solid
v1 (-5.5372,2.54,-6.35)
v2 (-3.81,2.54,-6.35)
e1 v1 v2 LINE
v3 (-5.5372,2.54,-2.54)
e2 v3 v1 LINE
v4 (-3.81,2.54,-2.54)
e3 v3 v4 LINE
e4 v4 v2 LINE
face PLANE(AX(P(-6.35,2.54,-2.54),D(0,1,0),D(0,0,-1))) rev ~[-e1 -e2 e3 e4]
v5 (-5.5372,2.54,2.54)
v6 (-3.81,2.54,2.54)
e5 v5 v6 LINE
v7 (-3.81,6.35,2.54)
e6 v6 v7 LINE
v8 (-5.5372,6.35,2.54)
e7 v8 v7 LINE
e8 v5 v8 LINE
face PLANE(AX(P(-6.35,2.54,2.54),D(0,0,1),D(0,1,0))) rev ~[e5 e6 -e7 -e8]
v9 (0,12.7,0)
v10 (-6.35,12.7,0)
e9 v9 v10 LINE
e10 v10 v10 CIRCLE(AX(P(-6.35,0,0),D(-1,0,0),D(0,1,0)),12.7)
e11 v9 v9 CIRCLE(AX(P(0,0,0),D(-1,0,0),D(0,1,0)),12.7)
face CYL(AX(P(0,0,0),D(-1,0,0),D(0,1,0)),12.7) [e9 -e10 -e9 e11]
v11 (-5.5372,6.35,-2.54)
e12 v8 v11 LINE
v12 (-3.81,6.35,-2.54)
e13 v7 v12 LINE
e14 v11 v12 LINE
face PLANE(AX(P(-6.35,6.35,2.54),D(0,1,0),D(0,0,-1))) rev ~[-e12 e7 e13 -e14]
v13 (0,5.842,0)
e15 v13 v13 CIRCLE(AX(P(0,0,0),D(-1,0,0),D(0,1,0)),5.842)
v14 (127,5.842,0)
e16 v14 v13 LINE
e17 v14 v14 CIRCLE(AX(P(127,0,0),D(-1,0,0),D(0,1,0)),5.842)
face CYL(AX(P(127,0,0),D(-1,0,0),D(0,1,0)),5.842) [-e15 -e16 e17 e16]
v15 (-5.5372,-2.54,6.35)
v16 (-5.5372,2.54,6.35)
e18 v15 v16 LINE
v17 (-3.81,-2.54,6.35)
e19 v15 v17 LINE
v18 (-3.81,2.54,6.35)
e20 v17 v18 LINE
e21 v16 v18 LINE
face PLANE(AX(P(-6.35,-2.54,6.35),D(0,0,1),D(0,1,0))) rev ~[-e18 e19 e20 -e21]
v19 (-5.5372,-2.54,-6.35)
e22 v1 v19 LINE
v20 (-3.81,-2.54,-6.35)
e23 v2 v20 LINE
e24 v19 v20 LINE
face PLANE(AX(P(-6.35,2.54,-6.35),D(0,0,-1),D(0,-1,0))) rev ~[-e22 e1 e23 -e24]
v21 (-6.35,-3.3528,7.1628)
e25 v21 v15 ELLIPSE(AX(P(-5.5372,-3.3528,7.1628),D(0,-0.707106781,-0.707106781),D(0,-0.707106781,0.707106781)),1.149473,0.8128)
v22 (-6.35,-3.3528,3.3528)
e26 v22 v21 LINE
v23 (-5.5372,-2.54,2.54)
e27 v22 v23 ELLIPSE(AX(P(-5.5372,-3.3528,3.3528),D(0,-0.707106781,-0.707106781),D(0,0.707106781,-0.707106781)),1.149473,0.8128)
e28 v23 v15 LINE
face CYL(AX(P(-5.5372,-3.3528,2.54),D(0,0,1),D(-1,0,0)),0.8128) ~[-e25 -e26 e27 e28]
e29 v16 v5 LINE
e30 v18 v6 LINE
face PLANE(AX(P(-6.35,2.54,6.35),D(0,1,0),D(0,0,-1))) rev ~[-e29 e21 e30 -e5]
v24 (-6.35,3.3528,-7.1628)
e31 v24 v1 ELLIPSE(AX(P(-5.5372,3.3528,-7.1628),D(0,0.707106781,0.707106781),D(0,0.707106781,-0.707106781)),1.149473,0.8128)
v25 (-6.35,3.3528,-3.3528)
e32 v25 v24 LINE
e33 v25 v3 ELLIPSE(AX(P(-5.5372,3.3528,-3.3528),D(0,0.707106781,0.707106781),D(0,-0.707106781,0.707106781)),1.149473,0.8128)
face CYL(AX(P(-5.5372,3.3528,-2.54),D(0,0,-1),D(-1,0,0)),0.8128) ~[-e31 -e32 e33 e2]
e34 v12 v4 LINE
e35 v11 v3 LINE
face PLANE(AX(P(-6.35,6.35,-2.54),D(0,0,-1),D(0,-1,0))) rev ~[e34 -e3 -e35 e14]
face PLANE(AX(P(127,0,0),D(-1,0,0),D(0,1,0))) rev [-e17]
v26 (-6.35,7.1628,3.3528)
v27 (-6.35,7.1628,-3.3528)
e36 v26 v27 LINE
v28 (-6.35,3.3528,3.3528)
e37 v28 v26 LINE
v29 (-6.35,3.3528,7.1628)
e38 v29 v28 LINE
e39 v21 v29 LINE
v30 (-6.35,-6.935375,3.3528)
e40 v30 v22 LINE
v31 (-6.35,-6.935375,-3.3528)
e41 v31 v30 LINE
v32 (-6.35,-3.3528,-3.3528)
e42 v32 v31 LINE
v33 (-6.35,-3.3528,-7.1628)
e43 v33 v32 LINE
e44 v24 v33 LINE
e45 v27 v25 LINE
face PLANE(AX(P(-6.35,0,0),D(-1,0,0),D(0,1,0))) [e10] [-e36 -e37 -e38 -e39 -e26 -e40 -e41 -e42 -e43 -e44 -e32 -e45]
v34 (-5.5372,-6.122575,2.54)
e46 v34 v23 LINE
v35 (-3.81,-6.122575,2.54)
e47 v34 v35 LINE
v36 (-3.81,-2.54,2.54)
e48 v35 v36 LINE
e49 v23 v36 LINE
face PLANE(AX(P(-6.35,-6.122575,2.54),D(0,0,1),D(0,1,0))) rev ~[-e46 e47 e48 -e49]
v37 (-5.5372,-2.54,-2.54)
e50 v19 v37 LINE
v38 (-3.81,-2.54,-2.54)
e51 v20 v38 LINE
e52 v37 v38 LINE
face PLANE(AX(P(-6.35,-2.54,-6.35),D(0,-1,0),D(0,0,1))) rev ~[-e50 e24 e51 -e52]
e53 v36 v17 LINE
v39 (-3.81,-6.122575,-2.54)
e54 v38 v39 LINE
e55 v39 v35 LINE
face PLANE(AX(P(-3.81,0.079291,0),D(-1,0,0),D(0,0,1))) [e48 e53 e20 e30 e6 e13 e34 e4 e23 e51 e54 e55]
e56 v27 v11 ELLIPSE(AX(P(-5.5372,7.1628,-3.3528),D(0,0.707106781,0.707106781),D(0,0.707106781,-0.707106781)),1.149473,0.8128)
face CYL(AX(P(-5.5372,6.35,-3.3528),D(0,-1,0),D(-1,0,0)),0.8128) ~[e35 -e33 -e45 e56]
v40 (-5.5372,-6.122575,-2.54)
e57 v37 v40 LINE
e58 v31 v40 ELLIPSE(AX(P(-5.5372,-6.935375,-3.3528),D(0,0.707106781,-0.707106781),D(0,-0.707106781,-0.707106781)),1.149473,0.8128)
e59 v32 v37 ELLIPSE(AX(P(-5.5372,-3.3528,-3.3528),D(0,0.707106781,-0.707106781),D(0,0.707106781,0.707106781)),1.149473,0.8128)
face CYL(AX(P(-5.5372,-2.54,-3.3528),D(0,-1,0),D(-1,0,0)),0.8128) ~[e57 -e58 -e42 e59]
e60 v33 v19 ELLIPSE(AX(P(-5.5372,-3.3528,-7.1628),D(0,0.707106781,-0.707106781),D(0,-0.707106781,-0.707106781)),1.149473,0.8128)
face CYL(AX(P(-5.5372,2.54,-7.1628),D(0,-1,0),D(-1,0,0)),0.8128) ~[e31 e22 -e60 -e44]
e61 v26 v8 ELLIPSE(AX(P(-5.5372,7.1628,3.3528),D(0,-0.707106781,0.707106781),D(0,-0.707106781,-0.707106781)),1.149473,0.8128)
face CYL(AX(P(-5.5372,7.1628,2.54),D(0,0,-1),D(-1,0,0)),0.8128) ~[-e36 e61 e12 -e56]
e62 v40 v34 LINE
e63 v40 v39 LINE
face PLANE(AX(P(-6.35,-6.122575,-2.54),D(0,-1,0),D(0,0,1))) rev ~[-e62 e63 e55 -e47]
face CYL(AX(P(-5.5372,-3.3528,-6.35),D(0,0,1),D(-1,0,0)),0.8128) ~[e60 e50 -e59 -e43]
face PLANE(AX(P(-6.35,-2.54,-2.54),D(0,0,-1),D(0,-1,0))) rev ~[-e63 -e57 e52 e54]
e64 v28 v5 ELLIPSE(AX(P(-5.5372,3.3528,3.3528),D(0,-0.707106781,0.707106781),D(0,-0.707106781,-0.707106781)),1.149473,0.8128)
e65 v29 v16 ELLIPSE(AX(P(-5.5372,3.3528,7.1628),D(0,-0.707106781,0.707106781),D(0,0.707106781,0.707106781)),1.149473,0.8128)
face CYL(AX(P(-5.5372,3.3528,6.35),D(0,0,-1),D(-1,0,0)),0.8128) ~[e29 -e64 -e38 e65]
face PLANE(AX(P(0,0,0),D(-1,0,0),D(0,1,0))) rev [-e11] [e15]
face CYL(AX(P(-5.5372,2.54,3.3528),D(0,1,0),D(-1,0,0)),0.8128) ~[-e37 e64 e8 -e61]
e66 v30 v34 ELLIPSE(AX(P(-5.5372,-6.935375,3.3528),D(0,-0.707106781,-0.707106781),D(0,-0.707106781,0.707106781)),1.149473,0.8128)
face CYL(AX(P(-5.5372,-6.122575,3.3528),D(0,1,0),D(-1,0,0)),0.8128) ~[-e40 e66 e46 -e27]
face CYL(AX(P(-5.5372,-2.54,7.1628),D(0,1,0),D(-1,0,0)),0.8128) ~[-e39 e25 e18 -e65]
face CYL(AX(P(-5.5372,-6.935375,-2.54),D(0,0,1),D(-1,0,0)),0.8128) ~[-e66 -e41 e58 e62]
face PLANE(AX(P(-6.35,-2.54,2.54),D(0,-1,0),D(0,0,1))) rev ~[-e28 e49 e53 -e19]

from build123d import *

# Parameters (mm, degrees)
CUT_EXTRUDE1_DEPTH = 2.54
FILLET2_R          = 0.8128


with BuildPart() as part:
    # Sketch1 → Revolve1 (revolve)
    with BuildSketch(Plane.XY):
        Polygon((0, 5.842), (0, 12.7), (-6.35, 12.7), (-6.35, 0), (0, 0), (127, 0), (127, 5.842), align=None)
    revolve(axis=Axis((127, 0, 0), (-1, 0, 0)))

    # Sketch2 → Cut-Extrude1 (cut)
    with BuildSketch(Plane.ZY.offset(6.35)):
        Polygon((-2.54, 6.35), (-2.54, 2.54), (-6.35, 2.54), (-6.35, -2.54), (-2.54, -2.54), (-2.54, -6.122575092), (2.54, -6.122575092), (2.54, -2.54), (6.35, -2.54), (6.35, 2.54), (2.54, 2.54), (2.54, 6.35), align=None)
    extrude(amount=-CUT_EXTRUDE1_DEPTH, mode=Mode.SUBTRACT)

    # Fillet2
    fillet2_edges = [part.edges().sort_by_distance(p)[0] for p in [
        (-6.35, 6.35, 0),
        (-6.35, 4.445, -2.54),
        (-6.35, 2.54, -4.445),
        (-6.35, 0, -6.35),
        (-6.35, -2.54, -4.445),
        (-6.35, -4.331287546, -2.54),
        (-6.35, -6.122575092, 0),
        (-6.35, -4.331287546, 2.54),
        (-6.35, -2.54, 4.445),
        (-6.35, 0, 6.35),
        (-6.35, 2.54, 4.445),
        (-6.35, 4.445, 2.54),
    ]]
    fillet(fillet2_edges, radius=FILLET2_R)


solid = part.part
